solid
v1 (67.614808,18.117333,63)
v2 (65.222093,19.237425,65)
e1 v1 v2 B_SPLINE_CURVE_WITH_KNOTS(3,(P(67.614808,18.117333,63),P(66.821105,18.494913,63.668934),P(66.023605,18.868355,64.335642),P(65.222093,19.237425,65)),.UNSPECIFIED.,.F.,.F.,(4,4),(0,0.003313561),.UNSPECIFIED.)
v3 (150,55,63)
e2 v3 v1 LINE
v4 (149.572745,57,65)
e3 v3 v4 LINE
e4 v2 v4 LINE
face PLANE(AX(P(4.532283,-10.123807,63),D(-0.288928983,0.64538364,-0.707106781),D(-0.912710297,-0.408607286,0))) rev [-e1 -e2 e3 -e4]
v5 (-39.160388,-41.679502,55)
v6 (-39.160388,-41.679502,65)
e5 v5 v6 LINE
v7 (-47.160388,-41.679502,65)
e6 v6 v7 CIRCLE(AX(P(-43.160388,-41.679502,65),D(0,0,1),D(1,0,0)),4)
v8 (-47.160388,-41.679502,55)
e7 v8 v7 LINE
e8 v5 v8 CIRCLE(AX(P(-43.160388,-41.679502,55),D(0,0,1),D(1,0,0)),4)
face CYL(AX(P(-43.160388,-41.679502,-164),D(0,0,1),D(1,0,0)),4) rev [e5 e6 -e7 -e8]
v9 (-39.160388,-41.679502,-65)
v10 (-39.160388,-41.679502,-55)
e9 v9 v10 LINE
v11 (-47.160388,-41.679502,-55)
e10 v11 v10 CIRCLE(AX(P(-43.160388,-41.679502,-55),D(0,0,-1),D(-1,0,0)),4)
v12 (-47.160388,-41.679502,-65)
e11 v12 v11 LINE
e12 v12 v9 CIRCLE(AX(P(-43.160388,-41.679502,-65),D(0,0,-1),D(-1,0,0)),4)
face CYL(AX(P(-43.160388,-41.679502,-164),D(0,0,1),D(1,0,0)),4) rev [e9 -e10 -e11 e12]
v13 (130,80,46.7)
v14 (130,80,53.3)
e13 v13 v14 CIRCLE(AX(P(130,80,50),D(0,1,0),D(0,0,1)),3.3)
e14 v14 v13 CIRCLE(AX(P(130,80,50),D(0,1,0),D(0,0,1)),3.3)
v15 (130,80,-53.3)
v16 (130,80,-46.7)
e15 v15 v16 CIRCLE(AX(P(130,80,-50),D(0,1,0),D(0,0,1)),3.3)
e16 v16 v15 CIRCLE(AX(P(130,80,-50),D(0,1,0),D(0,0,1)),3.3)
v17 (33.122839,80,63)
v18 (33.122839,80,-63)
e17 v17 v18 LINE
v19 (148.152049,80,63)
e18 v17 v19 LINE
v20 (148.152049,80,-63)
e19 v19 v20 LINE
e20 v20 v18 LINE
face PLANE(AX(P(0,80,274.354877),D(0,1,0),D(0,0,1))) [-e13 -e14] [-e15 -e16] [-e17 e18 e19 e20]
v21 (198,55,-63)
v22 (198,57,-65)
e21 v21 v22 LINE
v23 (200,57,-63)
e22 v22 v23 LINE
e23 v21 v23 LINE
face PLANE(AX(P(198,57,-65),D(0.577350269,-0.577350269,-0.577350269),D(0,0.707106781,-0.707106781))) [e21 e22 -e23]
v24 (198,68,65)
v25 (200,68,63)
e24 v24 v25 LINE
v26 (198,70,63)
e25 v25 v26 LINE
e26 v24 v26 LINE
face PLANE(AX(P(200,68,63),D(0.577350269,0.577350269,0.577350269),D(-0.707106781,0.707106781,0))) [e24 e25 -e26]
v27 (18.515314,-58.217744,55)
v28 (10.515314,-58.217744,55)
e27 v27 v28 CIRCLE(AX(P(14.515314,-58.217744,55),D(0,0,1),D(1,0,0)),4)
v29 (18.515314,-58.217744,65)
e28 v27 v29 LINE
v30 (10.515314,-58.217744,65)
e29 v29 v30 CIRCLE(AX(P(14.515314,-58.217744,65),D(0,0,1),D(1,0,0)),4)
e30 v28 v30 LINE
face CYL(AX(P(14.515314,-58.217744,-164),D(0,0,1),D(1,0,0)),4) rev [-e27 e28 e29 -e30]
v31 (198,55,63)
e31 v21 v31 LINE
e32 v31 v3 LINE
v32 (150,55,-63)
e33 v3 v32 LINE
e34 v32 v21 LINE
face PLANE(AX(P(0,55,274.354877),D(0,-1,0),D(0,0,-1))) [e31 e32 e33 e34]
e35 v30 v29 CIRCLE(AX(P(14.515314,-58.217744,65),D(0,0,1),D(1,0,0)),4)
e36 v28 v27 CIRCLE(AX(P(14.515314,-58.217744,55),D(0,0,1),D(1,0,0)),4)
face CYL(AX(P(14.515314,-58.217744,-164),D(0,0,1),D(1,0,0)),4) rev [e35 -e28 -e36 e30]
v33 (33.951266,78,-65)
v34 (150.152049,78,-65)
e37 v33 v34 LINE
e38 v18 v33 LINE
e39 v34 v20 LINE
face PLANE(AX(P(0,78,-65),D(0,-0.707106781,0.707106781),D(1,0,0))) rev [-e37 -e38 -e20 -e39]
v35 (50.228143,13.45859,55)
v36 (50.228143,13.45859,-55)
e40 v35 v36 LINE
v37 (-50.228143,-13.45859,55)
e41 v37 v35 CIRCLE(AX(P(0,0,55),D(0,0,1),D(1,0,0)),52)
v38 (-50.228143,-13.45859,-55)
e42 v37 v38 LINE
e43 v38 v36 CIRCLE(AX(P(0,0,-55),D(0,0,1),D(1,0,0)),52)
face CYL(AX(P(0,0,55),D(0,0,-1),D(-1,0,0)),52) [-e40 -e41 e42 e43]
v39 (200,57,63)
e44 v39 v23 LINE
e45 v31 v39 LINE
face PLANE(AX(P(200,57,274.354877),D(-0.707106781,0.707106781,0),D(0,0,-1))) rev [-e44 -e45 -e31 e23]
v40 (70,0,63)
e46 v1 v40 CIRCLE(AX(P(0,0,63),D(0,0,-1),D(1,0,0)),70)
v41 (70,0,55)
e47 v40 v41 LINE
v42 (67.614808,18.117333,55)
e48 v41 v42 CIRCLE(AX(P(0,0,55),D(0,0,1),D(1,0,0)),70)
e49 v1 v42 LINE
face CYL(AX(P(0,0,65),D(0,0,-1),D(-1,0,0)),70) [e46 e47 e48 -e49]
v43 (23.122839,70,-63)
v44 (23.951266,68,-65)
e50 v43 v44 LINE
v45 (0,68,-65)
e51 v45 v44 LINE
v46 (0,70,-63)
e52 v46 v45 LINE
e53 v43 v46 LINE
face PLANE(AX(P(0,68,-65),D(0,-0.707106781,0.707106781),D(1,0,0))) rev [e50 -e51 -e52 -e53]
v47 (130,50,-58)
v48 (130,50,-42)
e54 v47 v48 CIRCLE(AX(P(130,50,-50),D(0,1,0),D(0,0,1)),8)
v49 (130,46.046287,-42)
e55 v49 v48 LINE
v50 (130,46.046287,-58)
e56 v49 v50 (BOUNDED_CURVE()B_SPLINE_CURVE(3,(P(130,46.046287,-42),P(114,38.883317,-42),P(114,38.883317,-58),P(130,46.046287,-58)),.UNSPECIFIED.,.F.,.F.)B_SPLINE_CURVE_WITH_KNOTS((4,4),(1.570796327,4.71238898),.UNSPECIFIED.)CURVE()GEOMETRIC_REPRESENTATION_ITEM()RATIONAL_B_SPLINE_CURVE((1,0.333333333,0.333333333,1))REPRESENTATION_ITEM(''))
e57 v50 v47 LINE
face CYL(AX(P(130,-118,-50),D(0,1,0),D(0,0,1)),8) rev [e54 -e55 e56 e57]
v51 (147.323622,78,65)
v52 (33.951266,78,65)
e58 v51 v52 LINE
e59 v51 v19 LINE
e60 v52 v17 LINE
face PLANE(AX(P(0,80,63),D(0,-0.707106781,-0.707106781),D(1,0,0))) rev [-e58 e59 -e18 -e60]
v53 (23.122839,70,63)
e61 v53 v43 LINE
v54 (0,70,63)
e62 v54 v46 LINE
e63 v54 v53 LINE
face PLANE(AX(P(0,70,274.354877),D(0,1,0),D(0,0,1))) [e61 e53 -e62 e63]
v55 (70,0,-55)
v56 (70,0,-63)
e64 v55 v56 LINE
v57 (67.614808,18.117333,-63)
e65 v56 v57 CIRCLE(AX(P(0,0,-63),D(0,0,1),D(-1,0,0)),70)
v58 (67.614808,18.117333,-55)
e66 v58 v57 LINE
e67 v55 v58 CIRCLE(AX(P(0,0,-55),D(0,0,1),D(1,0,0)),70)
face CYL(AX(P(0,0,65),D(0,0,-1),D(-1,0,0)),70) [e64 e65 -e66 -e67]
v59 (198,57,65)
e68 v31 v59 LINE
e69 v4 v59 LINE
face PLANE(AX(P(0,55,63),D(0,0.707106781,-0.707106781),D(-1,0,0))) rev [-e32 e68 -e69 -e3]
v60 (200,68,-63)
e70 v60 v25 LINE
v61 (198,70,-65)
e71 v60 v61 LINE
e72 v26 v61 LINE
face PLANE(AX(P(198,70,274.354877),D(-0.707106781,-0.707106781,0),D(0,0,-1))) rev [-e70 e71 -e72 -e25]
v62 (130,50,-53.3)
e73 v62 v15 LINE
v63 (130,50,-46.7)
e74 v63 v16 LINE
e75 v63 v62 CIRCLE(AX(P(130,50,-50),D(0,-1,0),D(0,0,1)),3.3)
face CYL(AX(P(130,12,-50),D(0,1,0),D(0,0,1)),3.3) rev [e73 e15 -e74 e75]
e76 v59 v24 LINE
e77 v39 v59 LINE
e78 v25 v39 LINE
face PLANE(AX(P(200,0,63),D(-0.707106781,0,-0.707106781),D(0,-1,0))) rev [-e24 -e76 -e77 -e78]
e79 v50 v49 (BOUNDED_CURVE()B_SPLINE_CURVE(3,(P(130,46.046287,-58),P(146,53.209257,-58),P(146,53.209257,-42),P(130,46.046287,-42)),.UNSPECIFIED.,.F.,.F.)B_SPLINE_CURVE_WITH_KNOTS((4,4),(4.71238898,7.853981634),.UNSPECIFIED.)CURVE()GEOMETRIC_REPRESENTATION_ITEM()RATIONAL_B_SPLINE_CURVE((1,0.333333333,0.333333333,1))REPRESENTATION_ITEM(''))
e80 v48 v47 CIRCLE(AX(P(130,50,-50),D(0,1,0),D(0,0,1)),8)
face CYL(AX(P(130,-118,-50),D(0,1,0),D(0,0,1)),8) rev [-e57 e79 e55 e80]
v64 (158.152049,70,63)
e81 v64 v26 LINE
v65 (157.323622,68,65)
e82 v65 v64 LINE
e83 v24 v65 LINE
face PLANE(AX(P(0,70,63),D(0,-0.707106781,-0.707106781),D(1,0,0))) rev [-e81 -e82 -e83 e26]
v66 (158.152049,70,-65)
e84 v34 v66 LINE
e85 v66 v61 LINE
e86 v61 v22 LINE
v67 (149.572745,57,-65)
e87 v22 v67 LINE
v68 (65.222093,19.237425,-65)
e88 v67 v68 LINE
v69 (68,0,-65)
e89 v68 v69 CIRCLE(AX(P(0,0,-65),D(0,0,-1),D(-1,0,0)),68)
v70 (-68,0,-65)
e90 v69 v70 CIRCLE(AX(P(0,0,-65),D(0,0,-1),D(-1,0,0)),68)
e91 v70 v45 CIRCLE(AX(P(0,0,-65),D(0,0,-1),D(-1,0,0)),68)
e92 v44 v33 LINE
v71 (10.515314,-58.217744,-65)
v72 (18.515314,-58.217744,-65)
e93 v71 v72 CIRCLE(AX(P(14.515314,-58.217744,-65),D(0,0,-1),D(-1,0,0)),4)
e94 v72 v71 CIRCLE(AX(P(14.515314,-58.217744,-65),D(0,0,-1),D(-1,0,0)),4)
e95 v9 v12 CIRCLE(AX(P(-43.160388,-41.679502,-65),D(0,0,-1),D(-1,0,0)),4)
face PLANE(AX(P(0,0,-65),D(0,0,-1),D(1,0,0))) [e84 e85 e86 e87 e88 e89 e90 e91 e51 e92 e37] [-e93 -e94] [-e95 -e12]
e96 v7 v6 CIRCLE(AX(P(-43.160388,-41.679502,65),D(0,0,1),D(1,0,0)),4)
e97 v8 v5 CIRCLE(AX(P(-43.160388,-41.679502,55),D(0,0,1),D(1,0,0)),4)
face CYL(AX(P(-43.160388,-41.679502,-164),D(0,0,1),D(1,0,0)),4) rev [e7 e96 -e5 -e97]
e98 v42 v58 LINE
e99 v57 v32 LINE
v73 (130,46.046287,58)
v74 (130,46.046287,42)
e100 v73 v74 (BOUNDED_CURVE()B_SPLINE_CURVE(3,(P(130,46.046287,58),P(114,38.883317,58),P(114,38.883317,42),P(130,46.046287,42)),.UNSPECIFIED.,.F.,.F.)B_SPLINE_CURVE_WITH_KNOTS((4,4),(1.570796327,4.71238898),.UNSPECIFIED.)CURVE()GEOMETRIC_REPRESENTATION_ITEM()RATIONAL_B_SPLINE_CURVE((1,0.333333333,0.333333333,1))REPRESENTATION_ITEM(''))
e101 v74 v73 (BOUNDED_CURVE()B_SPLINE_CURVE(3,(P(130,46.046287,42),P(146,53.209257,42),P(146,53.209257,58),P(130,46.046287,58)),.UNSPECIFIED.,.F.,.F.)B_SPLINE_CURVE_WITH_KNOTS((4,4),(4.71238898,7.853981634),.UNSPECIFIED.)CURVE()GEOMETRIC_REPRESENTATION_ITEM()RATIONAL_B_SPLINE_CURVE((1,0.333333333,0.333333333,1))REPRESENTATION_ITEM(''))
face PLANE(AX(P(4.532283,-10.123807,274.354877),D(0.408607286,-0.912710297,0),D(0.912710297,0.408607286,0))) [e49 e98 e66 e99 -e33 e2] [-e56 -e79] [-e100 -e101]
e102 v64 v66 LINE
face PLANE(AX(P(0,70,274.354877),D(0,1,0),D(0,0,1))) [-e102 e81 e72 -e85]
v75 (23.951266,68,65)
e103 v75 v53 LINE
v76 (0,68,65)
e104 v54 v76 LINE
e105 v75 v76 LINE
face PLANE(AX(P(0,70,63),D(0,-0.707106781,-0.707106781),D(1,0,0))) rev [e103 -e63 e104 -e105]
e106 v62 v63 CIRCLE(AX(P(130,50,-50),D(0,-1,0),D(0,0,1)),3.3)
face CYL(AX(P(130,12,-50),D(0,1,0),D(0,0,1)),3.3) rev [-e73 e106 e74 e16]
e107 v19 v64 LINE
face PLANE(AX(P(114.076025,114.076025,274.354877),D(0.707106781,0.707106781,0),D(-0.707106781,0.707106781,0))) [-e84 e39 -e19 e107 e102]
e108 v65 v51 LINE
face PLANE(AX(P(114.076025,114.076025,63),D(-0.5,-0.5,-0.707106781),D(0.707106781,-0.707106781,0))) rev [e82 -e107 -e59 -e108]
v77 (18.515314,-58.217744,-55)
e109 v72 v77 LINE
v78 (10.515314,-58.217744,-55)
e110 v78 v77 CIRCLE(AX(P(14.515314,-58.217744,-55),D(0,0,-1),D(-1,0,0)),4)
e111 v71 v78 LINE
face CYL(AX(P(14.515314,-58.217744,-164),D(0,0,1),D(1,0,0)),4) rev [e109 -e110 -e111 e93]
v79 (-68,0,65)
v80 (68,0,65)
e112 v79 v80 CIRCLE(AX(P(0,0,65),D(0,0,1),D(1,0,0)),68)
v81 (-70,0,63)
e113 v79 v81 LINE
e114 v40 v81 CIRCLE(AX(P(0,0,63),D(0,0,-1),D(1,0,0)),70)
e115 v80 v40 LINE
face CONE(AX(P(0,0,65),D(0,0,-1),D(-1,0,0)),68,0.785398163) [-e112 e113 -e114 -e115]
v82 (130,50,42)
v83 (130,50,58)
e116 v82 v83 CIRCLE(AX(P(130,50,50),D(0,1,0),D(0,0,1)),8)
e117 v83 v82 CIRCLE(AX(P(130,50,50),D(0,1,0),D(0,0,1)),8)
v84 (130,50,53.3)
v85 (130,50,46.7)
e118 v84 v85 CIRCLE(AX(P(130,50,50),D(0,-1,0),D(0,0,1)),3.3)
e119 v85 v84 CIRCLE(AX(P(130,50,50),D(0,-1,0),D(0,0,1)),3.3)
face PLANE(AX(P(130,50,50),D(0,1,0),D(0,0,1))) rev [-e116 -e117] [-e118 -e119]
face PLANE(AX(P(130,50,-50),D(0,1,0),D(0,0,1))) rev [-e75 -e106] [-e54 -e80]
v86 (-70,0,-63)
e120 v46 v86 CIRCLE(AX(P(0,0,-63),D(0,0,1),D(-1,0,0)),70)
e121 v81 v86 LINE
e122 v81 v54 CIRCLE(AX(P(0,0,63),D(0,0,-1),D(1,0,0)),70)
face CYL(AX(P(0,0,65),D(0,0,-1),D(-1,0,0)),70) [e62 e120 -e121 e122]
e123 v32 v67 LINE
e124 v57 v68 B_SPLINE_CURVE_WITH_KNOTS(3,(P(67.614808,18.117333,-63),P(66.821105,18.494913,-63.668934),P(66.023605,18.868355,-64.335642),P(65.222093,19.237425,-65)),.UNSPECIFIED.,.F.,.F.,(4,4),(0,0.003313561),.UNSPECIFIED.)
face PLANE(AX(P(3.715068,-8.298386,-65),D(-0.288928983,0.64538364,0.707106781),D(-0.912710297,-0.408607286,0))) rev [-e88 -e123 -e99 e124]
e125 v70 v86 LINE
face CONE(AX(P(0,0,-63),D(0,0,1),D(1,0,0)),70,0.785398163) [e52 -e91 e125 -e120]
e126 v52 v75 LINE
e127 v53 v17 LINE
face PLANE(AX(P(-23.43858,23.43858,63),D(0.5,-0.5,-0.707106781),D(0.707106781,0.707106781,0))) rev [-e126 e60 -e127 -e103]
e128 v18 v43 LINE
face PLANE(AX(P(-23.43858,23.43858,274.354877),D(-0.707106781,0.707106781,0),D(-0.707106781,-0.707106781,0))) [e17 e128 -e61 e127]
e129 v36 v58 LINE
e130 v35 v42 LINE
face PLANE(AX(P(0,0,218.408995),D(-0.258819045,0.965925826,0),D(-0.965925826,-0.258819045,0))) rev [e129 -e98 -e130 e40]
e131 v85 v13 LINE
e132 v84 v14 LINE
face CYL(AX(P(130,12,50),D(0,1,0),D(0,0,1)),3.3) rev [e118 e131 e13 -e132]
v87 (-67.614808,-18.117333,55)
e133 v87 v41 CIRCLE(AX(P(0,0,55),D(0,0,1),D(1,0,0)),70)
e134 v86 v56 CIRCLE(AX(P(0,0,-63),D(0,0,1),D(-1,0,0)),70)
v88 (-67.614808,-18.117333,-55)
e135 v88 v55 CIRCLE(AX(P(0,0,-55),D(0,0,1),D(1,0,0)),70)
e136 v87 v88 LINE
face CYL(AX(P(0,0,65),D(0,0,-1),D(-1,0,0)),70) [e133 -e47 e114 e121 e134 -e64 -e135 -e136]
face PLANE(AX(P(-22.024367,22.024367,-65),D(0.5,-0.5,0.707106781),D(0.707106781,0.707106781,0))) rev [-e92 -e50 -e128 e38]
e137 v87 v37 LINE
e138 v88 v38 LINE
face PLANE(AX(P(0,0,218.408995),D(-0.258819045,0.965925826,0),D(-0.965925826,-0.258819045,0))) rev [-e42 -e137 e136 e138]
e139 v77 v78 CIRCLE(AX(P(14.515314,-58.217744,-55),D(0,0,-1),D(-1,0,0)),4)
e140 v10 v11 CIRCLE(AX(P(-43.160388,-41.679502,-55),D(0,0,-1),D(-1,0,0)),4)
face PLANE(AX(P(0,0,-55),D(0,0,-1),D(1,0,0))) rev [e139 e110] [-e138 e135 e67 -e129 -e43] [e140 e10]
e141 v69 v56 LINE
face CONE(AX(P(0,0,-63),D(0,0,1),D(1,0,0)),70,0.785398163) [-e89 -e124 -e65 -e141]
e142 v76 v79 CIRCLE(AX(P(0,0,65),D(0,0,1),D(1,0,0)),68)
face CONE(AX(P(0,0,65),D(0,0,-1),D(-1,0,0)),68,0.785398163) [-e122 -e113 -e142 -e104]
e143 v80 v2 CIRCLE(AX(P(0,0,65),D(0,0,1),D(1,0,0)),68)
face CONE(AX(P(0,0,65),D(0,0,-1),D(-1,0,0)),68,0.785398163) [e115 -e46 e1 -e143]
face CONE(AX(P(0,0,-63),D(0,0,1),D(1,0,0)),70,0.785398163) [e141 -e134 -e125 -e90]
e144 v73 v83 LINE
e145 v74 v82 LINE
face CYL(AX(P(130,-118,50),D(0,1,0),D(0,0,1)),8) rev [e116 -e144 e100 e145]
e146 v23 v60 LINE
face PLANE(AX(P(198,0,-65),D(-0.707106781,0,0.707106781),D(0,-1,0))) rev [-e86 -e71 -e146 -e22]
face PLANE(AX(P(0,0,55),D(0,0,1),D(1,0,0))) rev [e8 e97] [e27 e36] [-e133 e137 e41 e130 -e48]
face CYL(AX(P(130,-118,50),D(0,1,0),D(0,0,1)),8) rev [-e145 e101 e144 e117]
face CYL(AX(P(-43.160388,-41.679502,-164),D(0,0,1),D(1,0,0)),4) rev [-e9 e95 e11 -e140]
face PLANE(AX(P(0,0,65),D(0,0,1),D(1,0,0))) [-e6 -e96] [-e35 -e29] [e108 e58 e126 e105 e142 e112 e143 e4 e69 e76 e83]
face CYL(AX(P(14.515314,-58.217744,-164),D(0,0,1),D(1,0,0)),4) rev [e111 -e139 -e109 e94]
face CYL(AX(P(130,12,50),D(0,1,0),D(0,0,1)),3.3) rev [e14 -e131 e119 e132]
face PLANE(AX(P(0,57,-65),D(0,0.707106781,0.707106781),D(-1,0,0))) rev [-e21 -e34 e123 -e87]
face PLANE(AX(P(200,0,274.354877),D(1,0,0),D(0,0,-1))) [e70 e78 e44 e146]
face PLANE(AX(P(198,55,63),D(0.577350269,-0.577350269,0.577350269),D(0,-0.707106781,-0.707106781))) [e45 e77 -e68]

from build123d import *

# Parameters (mm, degrees)
SKETCH_1_R                  = 52
EXTRUDE_1_DEPTH             = 55
SKETCH_2_R                  = 70
EXTRUDE_2_DEPTH             = 10
EXTRUDE_START               = 110
EXTRUDE_3_DEPTH             = 110
EXTRUDE_4_REACH             = 120.427
EXTRUDE_4_DIRECTION_2_REACH = 120.427
SKETCH_5_R                  = 4
CUT_EXTRUDE_1_DEPTH         = 229
SKETCH_6_R                  = 3.3
CUT_EXTRUDE_2_DEPTH         = 68
CUT_EXTRUDE_START           = -30
SKETCH_8_R                  = 8
CUT_EXTRUDE_4_DEPTH         = 168
CHAMFER_1_SIZE              = 2


with BuildPart() as part:
    # 草图1 → 凸台-拉伸1 (new, symmetric)
    with BuildSketch(Plane.XY):
        Circle(SKETCH_1_R)
    extrude(amount=EXTRUDE_1_DEPTH, both=True)

    # 草图2 → 凸台-拉伸2 (add)
    with BuildSketch(Plane.XY.offset(55)):
        Circle(SKETCH_2_R)
    extrude(amount=EXTRUDE_2_DEPTH)

    # 镜向1: part across plane


with BuildPart() as part_1:
    add(part.part)
    add(part.part.mirror(Plane.XY))

    # 草图3 → 凸台-拉伸3 (add)
    with BuildSketch(Plane.XY.offset(-55).offset(EXTRUDE_START)):
        with BuildLine():
            ThreePointArc((67.61480784, 18.117333157), (-18.117333157, 67.61480784), (-67.61480784, -18.117333157))
            Line((-67.61480784, -18.117333157), (-50.228142967, -13.458590345))
            ThreePointArc((-50.228142967, -13.458590345), (-13.458590345, 50.228142967), (50.228142967, 13.458590345))
            Line((50.228142967, 13.458590345), (67.61480784, 18.117333157))
        make_face()
    extrude(amount=-EXTRUDE_3_DEPTH)

    # 凸台-拉伸4: up to this face of the body (flat: up to its plane)
    extrude_4_end = Plane(part_1.part.faces().sort_by_distance((0, 0, 65))[0])
    # 草图4 → 凸台-拉伸4 (add, up to the picked face)
    with BuildSketch(Plane.XY, mode=Mode.PRIVATE) as extrude_4_sk1:
        with BuildLine():
            Line((23.122839281, 70), (0, 70))
            ThreePointArc((0, 70), (42.613300031, 55.53473382), (67.61480784, 18.117333157))
            Line((67.61480784, 18.117333157), (150, 55))
            Line((150, 55), (200, 55))
            Line((200, 55), (200, 70))
            Line((200, 70), (158.152049004, 70))
            Line((158.152049004, 70), (23.122839281, 70))
        make_face()
    extrude_4_tool1 = split(extrude(extrude_4_sk1.sketch, amount=EXTRUDE_4_REACH, mode=Mode.PRIVATE), bisect_by=extrude_4_end, keep=Keep.BOTH, mode=Mode.PRIVATE)
    # 草图4 → 凸台-拉伸4 (add, up to the picked face)
    with BuildSketch(Plane.XY, mode=Mode.PRIVATE) as extrude_4_sk2:
        Polygon((33.122839281, 80), (23.122839281, 70), (158.152049004, 70), (148.152049004, 80), align=None)
    extrude_4_tool2 = split(extrude(extrude_4_sk2.sketch, amount=EXTRUDE_4_REACH, mode=Mode.PRIVATE), bisect_by=extrude_4_end, keep=Keep.BOTH, mode=Mode.PRIVATE)
    add(extrude_4_tool1.solids().sort_by(Axis((103.613169, 54.432495, 0), (0, 0, 1)))[0])
    add(extrude_4_tool2.solids().sort_by(Axis((90.637444, 74.866698, 0), (0, 0, 1)))[0])

    # 凸台-拉伸4 direction 2: up to this face of the body (flat: up to its plane)
    extrude_4_direction_2_end = Plane(part_1.part.faces().sort_by_distance((0, 0, -65))[0])
    # 草图4 → 凸台-拉伸4 direction 2 (add, up to the picked face)
    with BuildSketch(Plane.XY, mode=Mode.PRIVATE) as extrude_4_direction_2_sk1:
        with BuildLine():
            Line((23.122839281, 70), (0, 70))
            ThreePointArc((0, 70), (42.613300031, 55.53473382), (67.61480784, 18.117333157))
            Line((67.61480784, 18.117333157), (150, 55))
            Line((150, 55), (200, 55))
            Line((200, 55), (200, 70))
            Line((200, 70), (158.152049004, 70))
            Line((158.152049004, 70), (23.122839281, 70))
        make_face()
    extrude_4_direction_2_tool1 = split(extrude(extrude_4_direction_2_sk1.sketch, amount=-EXTRUDE_4_DIRECTION_2_REACH, mode=Mode.PRIVATE), bisect_by=extrude_4_direction_2_end, keep=Keep.BOTH, mode=Mode.PRIVATE)
    # 草图4 → 凸台-拉伸4 direction 2 (add, up to the picked face)
    with BuildSketch(Plane.XY, mode=Mode.PRIVATE) as extrude_4_direction_2_sk2:
        Polygon((33.122839281, 80), (23.122839281, 70), (158.152049004, 70), (148.152049004, 80), align=None)
    extrude_4_direction_2_tool2 = split(extrude(extrude_4_direction_2_sk2.sketch, amount=-EXTRUDE_4_DIRECTION_2_REACH, mode=Mode.PRIVATE), bisect_by=extrude_4_direction_2_end, keep=Keep.BOTH, mode=Mode.PRIVATE)
    add(extrude_4_direction_2_tool1.solids().sort_by(Axis((103.613169, 54.432495, 0), (0, 0, -1)))[0])
    add(extrude_4_direction_2_tool2.solids().sort_by(Axis((90.637444, 74.866698, 0), (0, 0, -1)))[0])

    # 草图5 → 切除-拉伸1 (cut)
    with BuildSketch(Plane.XY.offset(65)):
        with Locations(Location((-43.16038802, -41.679502228, 0), (0, 0, 180))):
            Circle(SKETCH_5_R)
        with Locations(Location((14.515313736, -58.217743577, 0), (0, 0, 180))):
            Circle(SKETCH_5_R)
    extrude(amount=-CUT_EXTRUDE_1_DEPTH, mode=Mode.SUBTRACT)

    # 草图6 → 切除-拉伸2 (cut)
    with BuildSketch(Plane(origin=(0, 80, 0), x_dir=(1, 0, 0), z_dir=(0, 1, 0))):
        with Locations(Location((130, 50, 0), (0, 0, 270))):
            Circle(SKETCH_6_R)
        with Locations(Location((130, -50, 0), (0, 0, 270))):
            Circle(SKETCH_6_R)
    extrude(amount=-CUT_EXTRUDE_2_DEPTH, mode=Mode.SUBTRACT)

    # 草图8 → 切除-拉伸4 (cut)
    with BuildSketch(Plane(origin=(0, 80, 0), x_dir=(1, 0, 0), z_dir=(0, 1, 0)).offset(CUT_EXTRUDE_START)):
        with Locations(Location((130, 50, 0), (0, 0, 270))):
            Circle(SKETCH_8_R)
        with Locations(Location((130, -50, 0), (0, 0, 270))):
            Circle(SKETCH_8_R)
    extrude(amount=-CUT_EXTRUDE_4_DEPTH, mode=Mode.SUBTRACT)

    # 倒角1
    chamfer_1_edges = [part_1.edges().sort_by_distance(p)[0] for p in [
        (-42.613300031, -55.53473382, -65),
        (-42.613300031, -55.53473382, 65),
        (11.561419641, 70, 65),
        (28.122839281, 75, 65),
        (90.637444143, 80, 65),
        (153.152049004, 75, 65),
        (179.076024502, 70, 65),
        (200, 70, 0),
        (200, 62.5, 65),
        (200, 55, 0),
        (175, 55, 65),
        (108.80740392, 36.558666579, 65),
        (108.80740392, 36.558666579, -65),
        (11.561419641, 70, -65),
        (28.122839281, 75, -65),
        (90.637444143, 80, -65),
        (200, 62.5, -65),
        (175, 55, -65),
    ]]
    chamfer(chamfer_1_edges, length=CHAMFER_1_SIZE)


solid = part_1.part
